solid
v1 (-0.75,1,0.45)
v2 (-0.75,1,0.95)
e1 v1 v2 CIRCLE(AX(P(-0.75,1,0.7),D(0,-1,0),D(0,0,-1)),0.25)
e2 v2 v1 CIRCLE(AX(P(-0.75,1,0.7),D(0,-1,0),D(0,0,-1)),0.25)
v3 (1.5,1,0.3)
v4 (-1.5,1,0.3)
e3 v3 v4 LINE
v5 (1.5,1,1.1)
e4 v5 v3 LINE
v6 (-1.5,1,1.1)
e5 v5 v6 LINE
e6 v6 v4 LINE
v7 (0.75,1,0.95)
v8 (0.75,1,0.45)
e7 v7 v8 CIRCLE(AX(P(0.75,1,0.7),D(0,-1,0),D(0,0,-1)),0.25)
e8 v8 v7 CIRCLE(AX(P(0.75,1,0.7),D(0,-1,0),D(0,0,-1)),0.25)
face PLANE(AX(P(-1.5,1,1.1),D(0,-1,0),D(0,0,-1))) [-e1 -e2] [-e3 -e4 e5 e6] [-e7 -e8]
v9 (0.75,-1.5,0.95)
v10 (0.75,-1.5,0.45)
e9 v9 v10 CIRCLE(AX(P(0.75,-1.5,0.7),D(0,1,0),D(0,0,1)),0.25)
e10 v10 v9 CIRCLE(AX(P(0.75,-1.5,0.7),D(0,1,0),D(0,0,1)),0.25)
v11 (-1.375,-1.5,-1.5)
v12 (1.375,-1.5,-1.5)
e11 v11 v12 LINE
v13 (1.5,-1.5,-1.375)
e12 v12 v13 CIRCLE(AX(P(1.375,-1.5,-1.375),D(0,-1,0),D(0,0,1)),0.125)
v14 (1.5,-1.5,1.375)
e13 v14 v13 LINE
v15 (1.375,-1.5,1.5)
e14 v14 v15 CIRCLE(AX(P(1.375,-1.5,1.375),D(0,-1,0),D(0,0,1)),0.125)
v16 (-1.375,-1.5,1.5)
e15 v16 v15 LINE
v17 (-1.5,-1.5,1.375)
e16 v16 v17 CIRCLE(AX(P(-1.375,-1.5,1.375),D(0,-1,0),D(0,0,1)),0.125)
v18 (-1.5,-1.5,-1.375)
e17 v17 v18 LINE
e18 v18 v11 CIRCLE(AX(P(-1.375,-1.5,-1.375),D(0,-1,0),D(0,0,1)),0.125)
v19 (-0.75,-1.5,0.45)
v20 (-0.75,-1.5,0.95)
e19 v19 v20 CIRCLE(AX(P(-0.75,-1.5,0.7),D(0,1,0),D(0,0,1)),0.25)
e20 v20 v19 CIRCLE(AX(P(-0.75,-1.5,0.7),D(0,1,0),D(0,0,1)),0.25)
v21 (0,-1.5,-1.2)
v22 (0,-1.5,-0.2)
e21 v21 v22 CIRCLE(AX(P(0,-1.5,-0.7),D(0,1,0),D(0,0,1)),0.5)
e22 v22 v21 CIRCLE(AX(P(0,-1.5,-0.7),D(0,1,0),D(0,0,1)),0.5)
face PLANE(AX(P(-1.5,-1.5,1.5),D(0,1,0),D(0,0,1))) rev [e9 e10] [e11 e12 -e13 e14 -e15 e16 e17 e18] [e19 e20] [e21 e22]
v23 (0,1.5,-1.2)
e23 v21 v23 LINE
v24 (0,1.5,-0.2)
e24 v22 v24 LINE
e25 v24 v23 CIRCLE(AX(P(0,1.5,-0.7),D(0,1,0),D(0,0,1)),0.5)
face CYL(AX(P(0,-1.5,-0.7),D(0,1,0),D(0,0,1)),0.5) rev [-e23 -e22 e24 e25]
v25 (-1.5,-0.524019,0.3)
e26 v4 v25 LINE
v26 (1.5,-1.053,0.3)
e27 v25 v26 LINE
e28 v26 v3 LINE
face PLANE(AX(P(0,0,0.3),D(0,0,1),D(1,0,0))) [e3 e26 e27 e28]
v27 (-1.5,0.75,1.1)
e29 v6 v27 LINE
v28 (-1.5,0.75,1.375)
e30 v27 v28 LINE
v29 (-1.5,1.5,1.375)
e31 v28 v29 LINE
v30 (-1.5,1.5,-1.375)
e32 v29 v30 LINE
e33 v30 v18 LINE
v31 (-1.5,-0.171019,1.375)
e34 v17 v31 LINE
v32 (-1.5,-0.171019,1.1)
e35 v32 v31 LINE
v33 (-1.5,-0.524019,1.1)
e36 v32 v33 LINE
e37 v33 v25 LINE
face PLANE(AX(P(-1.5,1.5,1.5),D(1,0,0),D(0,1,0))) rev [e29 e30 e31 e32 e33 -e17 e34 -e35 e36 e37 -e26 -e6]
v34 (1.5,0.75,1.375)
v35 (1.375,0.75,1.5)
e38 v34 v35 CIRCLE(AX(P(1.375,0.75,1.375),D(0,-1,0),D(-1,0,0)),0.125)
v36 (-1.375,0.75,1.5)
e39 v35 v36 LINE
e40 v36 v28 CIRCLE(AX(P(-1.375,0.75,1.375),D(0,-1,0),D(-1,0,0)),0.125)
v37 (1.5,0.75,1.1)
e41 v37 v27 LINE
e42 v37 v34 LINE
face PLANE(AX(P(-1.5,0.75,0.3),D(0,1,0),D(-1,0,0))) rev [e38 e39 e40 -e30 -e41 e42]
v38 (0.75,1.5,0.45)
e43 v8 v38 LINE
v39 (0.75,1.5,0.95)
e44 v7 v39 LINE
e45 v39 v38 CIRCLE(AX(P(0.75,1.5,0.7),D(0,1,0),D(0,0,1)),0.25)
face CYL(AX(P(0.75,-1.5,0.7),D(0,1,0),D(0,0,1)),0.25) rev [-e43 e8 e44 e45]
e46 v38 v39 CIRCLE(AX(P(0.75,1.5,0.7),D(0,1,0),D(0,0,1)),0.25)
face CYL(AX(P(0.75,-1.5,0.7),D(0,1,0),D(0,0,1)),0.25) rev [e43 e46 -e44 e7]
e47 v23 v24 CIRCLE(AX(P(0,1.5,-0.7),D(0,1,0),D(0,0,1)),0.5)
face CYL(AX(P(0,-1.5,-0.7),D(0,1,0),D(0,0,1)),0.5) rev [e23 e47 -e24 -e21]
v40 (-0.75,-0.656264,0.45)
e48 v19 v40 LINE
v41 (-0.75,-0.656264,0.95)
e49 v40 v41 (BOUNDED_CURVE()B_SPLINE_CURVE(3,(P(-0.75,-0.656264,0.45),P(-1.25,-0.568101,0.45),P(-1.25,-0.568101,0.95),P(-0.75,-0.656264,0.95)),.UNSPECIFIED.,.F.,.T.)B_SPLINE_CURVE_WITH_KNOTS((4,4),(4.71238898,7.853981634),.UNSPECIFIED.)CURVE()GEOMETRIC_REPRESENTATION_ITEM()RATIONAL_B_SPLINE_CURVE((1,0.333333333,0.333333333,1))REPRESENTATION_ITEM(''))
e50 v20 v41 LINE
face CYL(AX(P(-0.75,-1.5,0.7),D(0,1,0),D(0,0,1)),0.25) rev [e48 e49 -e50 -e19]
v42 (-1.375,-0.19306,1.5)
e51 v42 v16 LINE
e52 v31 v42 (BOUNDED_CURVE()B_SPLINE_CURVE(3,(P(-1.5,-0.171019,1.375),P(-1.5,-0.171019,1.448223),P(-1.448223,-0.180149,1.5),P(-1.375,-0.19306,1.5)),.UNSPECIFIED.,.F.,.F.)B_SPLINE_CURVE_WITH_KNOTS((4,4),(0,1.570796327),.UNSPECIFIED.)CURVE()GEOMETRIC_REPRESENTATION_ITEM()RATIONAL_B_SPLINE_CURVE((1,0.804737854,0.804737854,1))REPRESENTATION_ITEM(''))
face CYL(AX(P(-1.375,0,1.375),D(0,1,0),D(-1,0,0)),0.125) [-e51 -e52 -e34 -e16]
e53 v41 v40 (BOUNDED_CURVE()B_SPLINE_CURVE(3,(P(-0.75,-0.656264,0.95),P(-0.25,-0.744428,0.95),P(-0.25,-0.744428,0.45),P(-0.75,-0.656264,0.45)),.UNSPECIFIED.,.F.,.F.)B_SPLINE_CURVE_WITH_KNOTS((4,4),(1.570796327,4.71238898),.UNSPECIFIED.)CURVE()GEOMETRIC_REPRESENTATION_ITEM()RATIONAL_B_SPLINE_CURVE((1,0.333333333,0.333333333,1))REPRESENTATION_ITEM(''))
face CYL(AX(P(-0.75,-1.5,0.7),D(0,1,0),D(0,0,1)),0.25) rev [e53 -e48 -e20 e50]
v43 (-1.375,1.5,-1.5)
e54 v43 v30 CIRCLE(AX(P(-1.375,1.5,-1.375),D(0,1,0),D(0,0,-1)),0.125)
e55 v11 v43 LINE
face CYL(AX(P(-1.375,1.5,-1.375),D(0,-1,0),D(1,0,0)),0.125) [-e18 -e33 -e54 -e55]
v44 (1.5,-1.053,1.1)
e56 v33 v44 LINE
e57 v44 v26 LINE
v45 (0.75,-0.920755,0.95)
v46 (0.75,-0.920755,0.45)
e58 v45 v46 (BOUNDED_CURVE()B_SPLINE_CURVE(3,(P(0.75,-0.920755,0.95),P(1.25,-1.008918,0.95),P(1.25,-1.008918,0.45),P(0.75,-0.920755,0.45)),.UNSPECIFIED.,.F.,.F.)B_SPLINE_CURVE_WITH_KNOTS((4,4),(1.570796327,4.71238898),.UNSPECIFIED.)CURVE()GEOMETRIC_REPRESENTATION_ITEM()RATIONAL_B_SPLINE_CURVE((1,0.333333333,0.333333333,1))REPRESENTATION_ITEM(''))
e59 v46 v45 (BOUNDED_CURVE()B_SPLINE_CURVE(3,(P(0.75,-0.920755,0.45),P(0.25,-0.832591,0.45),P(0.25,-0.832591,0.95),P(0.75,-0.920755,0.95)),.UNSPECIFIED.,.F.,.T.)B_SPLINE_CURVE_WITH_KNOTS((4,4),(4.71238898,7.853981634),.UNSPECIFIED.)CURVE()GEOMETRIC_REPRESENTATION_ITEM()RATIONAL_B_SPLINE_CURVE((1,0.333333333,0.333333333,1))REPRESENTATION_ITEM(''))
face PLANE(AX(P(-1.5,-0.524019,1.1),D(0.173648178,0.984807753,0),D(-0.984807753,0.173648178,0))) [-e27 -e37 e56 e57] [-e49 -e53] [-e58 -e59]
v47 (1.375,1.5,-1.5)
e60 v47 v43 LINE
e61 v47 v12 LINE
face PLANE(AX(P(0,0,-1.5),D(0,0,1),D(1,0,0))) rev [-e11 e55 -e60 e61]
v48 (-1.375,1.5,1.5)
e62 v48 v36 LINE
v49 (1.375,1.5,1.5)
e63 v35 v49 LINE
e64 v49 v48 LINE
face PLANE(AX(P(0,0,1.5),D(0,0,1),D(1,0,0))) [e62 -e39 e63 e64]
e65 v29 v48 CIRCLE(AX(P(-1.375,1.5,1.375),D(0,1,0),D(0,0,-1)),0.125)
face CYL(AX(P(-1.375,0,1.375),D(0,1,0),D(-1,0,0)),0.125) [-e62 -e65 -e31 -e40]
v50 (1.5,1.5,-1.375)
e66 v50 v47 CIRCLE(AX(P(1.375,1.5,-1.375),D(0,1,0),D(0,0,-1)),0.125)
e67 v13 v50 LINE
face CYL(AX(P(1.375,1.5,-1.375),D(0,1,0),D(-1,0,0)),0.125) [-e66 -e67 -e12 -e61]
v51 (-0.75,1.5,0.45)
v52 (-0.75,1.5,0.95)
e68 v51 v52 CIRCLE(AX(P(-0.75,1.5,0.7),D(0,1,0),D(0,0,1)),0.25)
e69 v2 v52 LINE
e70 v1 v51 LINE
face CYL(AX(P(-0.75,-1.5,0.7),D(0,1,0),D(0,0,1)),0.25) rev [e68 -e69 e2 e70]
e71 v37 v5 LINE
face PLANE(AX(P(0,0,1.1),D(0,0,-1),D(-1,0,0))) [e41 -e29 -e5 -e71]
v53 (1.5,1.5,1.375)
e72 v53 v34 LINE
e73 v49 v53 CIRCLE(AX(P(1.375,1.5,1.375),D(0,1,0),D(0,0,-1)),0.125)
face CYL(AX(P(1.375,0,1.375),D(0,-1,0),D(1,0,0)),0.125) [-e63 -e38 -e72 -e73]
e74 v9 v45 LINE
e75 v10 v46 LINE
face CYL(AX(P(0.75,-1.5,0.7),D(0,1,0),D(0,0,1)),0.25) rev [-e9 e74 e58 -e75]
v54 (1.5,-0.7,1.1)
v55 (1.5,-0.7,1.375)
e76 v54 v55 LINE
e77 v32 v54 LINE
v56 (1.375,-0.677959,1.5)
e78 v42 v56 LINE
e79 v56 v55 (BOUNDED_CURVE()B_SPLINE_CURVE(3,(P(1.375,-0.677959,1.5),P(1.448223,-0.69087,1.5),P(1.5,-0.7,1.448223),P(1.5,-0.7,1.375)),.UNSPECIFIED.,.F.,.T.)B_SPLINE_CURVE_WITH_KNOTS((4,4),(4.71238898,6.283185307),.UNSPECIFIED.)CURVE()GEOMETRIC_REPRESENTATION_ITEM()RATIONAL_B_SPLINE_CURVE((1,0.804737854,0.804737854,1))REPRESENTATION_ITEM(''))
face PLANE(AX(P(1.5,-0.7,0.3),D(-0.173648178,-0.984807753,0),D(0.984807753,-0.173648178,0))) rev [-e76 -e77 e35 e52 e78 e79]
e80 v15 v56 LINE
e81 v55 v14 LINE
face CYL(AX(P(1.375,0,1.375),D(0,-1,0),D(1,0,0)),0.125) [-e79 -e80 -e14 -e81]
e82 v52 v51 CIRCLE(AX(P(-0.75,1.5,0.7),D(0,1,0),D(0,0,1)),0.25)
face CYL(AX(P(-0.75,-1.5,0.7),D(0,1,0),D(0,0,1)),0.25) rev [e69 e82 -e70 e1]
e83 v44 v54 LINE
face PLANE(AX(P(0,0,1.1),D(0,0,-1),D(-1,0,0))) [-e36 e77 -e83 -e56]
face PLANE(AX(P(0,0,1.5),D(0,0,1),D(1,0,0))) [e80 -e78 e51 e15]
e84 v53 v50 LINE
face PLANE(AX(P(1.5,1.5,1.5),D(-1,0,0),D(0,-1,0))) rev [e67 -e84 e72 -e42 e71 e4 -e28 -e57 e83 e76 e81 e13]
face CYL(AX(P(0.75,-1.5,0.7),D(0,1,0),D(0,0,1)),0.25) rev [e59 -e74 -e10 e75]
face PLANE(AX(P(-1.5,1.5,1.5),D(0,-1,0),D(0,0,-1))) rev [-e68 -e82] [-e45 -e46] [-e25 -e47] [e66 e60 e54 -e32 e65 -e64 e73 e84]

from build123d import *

# Parameters (mm, degrees)
C_PROFILE_SKETCH_W         = 3
C_PROFILE_SKETCH_H         = 3
C_BODY_EXTRUDE_3MM_DEPTH   = 1.5
ANGLED_JAW_CUT_10DEG_DEPTH = 1.2
JAW_NOTCH_CUT_DEPTH        = 0.8
EDGE_FILLETS_R0_125_R      = 0.125
MOUNTING_HOLES_SKETCH_R    = 0.5
MOUNTING_HOLES_SKETCH_R_2  = 0.25
MOUNTING_HOLES_3X_DEPTH    = 4.674234614


with BuildPart() as part:
    # C-Profile Sketch → C-Body Extrude 3mm (new, symmetric)
    with BuildSketch(Plane.XY):
        Rectangle(C_PROFILE_SKETCH_W, C_PROFILE_SKETCH_H)
    extrude(amount=C_BODY_EXTRUDE_3MM_DEPTH, both=True)

    # Angled Jaw Sketch → Angled Jaw Cut 10deg (cut)
    with BuildSketch(Plane.XY.offset(1.5)):
        Polygon((1.5, -0.7), (-1.5, -0.171019058), (-1.5, 0.75), (1.5, 0.75), align=None)
    extrude(amount=-ANGLED_JAW_CUT_10DEG_DEPTH, mode=Mode.SUBTRACT)

    # Jaw Notch Sketch → Jaw Notch Cut (cut)
    with BuildSketch(Plane.XY.offset(0.3)):
        Polygon((1.5, -0.7), (1.5, -1.053), (-1.5, -0.524019058), (-1.5, 1), (1.5, 1), align=None)
    extrude(amount=JAW_NOTCH_CUT_DEPTH, mode=Mode.SUBTRACT)

    # Edge Fillets R0.125
    edge_fillets_r0_125_edges = [part.edges().sort_by_distance(p)[0] for p in [
        (-1.5, 1.125, 1.5),
        (-1.5, -0.835509529, 1.5),
        (1.5, 1.125, 1.5),
        (1.5, -1.1, 1.5),
        (-1.5, 0, -1.5),
        (1.5, 0, -1.5),
    ]]
    fillet(edge_fillets_r0_125_edges, radius=EDGE_FILLETS_R0_125_R)

    # Mounting Holes Sketch → Mounting Holes 3x (cut, through all)
    with BuildSketch(Plane(origin=(0, 1.5, 0), x_dir=(1, 0, 0), z_dir=(0, 1, 0))):
        with Locations(Location((0, 0.7, 0), (0, 0, 270))):
            Circle(MOUNTING_HOLES_SKETCH_R)
        with Locations(Location((0.75, -0.7, 0), (0, 0, 270))):
            Circle(MOUNTING_HOLES_SKETCH_R_2)
        with Locations(Location((-0.75, -0.7, 0), (0, 0, 270))):
            Circle(MOUNTING_HOLES_SKETCH_R_2)
    extrude(amount=-MOUNTING_HOLES_3X_DEPTH, mode=Mode.SUBTRACT)


solid = part.part
